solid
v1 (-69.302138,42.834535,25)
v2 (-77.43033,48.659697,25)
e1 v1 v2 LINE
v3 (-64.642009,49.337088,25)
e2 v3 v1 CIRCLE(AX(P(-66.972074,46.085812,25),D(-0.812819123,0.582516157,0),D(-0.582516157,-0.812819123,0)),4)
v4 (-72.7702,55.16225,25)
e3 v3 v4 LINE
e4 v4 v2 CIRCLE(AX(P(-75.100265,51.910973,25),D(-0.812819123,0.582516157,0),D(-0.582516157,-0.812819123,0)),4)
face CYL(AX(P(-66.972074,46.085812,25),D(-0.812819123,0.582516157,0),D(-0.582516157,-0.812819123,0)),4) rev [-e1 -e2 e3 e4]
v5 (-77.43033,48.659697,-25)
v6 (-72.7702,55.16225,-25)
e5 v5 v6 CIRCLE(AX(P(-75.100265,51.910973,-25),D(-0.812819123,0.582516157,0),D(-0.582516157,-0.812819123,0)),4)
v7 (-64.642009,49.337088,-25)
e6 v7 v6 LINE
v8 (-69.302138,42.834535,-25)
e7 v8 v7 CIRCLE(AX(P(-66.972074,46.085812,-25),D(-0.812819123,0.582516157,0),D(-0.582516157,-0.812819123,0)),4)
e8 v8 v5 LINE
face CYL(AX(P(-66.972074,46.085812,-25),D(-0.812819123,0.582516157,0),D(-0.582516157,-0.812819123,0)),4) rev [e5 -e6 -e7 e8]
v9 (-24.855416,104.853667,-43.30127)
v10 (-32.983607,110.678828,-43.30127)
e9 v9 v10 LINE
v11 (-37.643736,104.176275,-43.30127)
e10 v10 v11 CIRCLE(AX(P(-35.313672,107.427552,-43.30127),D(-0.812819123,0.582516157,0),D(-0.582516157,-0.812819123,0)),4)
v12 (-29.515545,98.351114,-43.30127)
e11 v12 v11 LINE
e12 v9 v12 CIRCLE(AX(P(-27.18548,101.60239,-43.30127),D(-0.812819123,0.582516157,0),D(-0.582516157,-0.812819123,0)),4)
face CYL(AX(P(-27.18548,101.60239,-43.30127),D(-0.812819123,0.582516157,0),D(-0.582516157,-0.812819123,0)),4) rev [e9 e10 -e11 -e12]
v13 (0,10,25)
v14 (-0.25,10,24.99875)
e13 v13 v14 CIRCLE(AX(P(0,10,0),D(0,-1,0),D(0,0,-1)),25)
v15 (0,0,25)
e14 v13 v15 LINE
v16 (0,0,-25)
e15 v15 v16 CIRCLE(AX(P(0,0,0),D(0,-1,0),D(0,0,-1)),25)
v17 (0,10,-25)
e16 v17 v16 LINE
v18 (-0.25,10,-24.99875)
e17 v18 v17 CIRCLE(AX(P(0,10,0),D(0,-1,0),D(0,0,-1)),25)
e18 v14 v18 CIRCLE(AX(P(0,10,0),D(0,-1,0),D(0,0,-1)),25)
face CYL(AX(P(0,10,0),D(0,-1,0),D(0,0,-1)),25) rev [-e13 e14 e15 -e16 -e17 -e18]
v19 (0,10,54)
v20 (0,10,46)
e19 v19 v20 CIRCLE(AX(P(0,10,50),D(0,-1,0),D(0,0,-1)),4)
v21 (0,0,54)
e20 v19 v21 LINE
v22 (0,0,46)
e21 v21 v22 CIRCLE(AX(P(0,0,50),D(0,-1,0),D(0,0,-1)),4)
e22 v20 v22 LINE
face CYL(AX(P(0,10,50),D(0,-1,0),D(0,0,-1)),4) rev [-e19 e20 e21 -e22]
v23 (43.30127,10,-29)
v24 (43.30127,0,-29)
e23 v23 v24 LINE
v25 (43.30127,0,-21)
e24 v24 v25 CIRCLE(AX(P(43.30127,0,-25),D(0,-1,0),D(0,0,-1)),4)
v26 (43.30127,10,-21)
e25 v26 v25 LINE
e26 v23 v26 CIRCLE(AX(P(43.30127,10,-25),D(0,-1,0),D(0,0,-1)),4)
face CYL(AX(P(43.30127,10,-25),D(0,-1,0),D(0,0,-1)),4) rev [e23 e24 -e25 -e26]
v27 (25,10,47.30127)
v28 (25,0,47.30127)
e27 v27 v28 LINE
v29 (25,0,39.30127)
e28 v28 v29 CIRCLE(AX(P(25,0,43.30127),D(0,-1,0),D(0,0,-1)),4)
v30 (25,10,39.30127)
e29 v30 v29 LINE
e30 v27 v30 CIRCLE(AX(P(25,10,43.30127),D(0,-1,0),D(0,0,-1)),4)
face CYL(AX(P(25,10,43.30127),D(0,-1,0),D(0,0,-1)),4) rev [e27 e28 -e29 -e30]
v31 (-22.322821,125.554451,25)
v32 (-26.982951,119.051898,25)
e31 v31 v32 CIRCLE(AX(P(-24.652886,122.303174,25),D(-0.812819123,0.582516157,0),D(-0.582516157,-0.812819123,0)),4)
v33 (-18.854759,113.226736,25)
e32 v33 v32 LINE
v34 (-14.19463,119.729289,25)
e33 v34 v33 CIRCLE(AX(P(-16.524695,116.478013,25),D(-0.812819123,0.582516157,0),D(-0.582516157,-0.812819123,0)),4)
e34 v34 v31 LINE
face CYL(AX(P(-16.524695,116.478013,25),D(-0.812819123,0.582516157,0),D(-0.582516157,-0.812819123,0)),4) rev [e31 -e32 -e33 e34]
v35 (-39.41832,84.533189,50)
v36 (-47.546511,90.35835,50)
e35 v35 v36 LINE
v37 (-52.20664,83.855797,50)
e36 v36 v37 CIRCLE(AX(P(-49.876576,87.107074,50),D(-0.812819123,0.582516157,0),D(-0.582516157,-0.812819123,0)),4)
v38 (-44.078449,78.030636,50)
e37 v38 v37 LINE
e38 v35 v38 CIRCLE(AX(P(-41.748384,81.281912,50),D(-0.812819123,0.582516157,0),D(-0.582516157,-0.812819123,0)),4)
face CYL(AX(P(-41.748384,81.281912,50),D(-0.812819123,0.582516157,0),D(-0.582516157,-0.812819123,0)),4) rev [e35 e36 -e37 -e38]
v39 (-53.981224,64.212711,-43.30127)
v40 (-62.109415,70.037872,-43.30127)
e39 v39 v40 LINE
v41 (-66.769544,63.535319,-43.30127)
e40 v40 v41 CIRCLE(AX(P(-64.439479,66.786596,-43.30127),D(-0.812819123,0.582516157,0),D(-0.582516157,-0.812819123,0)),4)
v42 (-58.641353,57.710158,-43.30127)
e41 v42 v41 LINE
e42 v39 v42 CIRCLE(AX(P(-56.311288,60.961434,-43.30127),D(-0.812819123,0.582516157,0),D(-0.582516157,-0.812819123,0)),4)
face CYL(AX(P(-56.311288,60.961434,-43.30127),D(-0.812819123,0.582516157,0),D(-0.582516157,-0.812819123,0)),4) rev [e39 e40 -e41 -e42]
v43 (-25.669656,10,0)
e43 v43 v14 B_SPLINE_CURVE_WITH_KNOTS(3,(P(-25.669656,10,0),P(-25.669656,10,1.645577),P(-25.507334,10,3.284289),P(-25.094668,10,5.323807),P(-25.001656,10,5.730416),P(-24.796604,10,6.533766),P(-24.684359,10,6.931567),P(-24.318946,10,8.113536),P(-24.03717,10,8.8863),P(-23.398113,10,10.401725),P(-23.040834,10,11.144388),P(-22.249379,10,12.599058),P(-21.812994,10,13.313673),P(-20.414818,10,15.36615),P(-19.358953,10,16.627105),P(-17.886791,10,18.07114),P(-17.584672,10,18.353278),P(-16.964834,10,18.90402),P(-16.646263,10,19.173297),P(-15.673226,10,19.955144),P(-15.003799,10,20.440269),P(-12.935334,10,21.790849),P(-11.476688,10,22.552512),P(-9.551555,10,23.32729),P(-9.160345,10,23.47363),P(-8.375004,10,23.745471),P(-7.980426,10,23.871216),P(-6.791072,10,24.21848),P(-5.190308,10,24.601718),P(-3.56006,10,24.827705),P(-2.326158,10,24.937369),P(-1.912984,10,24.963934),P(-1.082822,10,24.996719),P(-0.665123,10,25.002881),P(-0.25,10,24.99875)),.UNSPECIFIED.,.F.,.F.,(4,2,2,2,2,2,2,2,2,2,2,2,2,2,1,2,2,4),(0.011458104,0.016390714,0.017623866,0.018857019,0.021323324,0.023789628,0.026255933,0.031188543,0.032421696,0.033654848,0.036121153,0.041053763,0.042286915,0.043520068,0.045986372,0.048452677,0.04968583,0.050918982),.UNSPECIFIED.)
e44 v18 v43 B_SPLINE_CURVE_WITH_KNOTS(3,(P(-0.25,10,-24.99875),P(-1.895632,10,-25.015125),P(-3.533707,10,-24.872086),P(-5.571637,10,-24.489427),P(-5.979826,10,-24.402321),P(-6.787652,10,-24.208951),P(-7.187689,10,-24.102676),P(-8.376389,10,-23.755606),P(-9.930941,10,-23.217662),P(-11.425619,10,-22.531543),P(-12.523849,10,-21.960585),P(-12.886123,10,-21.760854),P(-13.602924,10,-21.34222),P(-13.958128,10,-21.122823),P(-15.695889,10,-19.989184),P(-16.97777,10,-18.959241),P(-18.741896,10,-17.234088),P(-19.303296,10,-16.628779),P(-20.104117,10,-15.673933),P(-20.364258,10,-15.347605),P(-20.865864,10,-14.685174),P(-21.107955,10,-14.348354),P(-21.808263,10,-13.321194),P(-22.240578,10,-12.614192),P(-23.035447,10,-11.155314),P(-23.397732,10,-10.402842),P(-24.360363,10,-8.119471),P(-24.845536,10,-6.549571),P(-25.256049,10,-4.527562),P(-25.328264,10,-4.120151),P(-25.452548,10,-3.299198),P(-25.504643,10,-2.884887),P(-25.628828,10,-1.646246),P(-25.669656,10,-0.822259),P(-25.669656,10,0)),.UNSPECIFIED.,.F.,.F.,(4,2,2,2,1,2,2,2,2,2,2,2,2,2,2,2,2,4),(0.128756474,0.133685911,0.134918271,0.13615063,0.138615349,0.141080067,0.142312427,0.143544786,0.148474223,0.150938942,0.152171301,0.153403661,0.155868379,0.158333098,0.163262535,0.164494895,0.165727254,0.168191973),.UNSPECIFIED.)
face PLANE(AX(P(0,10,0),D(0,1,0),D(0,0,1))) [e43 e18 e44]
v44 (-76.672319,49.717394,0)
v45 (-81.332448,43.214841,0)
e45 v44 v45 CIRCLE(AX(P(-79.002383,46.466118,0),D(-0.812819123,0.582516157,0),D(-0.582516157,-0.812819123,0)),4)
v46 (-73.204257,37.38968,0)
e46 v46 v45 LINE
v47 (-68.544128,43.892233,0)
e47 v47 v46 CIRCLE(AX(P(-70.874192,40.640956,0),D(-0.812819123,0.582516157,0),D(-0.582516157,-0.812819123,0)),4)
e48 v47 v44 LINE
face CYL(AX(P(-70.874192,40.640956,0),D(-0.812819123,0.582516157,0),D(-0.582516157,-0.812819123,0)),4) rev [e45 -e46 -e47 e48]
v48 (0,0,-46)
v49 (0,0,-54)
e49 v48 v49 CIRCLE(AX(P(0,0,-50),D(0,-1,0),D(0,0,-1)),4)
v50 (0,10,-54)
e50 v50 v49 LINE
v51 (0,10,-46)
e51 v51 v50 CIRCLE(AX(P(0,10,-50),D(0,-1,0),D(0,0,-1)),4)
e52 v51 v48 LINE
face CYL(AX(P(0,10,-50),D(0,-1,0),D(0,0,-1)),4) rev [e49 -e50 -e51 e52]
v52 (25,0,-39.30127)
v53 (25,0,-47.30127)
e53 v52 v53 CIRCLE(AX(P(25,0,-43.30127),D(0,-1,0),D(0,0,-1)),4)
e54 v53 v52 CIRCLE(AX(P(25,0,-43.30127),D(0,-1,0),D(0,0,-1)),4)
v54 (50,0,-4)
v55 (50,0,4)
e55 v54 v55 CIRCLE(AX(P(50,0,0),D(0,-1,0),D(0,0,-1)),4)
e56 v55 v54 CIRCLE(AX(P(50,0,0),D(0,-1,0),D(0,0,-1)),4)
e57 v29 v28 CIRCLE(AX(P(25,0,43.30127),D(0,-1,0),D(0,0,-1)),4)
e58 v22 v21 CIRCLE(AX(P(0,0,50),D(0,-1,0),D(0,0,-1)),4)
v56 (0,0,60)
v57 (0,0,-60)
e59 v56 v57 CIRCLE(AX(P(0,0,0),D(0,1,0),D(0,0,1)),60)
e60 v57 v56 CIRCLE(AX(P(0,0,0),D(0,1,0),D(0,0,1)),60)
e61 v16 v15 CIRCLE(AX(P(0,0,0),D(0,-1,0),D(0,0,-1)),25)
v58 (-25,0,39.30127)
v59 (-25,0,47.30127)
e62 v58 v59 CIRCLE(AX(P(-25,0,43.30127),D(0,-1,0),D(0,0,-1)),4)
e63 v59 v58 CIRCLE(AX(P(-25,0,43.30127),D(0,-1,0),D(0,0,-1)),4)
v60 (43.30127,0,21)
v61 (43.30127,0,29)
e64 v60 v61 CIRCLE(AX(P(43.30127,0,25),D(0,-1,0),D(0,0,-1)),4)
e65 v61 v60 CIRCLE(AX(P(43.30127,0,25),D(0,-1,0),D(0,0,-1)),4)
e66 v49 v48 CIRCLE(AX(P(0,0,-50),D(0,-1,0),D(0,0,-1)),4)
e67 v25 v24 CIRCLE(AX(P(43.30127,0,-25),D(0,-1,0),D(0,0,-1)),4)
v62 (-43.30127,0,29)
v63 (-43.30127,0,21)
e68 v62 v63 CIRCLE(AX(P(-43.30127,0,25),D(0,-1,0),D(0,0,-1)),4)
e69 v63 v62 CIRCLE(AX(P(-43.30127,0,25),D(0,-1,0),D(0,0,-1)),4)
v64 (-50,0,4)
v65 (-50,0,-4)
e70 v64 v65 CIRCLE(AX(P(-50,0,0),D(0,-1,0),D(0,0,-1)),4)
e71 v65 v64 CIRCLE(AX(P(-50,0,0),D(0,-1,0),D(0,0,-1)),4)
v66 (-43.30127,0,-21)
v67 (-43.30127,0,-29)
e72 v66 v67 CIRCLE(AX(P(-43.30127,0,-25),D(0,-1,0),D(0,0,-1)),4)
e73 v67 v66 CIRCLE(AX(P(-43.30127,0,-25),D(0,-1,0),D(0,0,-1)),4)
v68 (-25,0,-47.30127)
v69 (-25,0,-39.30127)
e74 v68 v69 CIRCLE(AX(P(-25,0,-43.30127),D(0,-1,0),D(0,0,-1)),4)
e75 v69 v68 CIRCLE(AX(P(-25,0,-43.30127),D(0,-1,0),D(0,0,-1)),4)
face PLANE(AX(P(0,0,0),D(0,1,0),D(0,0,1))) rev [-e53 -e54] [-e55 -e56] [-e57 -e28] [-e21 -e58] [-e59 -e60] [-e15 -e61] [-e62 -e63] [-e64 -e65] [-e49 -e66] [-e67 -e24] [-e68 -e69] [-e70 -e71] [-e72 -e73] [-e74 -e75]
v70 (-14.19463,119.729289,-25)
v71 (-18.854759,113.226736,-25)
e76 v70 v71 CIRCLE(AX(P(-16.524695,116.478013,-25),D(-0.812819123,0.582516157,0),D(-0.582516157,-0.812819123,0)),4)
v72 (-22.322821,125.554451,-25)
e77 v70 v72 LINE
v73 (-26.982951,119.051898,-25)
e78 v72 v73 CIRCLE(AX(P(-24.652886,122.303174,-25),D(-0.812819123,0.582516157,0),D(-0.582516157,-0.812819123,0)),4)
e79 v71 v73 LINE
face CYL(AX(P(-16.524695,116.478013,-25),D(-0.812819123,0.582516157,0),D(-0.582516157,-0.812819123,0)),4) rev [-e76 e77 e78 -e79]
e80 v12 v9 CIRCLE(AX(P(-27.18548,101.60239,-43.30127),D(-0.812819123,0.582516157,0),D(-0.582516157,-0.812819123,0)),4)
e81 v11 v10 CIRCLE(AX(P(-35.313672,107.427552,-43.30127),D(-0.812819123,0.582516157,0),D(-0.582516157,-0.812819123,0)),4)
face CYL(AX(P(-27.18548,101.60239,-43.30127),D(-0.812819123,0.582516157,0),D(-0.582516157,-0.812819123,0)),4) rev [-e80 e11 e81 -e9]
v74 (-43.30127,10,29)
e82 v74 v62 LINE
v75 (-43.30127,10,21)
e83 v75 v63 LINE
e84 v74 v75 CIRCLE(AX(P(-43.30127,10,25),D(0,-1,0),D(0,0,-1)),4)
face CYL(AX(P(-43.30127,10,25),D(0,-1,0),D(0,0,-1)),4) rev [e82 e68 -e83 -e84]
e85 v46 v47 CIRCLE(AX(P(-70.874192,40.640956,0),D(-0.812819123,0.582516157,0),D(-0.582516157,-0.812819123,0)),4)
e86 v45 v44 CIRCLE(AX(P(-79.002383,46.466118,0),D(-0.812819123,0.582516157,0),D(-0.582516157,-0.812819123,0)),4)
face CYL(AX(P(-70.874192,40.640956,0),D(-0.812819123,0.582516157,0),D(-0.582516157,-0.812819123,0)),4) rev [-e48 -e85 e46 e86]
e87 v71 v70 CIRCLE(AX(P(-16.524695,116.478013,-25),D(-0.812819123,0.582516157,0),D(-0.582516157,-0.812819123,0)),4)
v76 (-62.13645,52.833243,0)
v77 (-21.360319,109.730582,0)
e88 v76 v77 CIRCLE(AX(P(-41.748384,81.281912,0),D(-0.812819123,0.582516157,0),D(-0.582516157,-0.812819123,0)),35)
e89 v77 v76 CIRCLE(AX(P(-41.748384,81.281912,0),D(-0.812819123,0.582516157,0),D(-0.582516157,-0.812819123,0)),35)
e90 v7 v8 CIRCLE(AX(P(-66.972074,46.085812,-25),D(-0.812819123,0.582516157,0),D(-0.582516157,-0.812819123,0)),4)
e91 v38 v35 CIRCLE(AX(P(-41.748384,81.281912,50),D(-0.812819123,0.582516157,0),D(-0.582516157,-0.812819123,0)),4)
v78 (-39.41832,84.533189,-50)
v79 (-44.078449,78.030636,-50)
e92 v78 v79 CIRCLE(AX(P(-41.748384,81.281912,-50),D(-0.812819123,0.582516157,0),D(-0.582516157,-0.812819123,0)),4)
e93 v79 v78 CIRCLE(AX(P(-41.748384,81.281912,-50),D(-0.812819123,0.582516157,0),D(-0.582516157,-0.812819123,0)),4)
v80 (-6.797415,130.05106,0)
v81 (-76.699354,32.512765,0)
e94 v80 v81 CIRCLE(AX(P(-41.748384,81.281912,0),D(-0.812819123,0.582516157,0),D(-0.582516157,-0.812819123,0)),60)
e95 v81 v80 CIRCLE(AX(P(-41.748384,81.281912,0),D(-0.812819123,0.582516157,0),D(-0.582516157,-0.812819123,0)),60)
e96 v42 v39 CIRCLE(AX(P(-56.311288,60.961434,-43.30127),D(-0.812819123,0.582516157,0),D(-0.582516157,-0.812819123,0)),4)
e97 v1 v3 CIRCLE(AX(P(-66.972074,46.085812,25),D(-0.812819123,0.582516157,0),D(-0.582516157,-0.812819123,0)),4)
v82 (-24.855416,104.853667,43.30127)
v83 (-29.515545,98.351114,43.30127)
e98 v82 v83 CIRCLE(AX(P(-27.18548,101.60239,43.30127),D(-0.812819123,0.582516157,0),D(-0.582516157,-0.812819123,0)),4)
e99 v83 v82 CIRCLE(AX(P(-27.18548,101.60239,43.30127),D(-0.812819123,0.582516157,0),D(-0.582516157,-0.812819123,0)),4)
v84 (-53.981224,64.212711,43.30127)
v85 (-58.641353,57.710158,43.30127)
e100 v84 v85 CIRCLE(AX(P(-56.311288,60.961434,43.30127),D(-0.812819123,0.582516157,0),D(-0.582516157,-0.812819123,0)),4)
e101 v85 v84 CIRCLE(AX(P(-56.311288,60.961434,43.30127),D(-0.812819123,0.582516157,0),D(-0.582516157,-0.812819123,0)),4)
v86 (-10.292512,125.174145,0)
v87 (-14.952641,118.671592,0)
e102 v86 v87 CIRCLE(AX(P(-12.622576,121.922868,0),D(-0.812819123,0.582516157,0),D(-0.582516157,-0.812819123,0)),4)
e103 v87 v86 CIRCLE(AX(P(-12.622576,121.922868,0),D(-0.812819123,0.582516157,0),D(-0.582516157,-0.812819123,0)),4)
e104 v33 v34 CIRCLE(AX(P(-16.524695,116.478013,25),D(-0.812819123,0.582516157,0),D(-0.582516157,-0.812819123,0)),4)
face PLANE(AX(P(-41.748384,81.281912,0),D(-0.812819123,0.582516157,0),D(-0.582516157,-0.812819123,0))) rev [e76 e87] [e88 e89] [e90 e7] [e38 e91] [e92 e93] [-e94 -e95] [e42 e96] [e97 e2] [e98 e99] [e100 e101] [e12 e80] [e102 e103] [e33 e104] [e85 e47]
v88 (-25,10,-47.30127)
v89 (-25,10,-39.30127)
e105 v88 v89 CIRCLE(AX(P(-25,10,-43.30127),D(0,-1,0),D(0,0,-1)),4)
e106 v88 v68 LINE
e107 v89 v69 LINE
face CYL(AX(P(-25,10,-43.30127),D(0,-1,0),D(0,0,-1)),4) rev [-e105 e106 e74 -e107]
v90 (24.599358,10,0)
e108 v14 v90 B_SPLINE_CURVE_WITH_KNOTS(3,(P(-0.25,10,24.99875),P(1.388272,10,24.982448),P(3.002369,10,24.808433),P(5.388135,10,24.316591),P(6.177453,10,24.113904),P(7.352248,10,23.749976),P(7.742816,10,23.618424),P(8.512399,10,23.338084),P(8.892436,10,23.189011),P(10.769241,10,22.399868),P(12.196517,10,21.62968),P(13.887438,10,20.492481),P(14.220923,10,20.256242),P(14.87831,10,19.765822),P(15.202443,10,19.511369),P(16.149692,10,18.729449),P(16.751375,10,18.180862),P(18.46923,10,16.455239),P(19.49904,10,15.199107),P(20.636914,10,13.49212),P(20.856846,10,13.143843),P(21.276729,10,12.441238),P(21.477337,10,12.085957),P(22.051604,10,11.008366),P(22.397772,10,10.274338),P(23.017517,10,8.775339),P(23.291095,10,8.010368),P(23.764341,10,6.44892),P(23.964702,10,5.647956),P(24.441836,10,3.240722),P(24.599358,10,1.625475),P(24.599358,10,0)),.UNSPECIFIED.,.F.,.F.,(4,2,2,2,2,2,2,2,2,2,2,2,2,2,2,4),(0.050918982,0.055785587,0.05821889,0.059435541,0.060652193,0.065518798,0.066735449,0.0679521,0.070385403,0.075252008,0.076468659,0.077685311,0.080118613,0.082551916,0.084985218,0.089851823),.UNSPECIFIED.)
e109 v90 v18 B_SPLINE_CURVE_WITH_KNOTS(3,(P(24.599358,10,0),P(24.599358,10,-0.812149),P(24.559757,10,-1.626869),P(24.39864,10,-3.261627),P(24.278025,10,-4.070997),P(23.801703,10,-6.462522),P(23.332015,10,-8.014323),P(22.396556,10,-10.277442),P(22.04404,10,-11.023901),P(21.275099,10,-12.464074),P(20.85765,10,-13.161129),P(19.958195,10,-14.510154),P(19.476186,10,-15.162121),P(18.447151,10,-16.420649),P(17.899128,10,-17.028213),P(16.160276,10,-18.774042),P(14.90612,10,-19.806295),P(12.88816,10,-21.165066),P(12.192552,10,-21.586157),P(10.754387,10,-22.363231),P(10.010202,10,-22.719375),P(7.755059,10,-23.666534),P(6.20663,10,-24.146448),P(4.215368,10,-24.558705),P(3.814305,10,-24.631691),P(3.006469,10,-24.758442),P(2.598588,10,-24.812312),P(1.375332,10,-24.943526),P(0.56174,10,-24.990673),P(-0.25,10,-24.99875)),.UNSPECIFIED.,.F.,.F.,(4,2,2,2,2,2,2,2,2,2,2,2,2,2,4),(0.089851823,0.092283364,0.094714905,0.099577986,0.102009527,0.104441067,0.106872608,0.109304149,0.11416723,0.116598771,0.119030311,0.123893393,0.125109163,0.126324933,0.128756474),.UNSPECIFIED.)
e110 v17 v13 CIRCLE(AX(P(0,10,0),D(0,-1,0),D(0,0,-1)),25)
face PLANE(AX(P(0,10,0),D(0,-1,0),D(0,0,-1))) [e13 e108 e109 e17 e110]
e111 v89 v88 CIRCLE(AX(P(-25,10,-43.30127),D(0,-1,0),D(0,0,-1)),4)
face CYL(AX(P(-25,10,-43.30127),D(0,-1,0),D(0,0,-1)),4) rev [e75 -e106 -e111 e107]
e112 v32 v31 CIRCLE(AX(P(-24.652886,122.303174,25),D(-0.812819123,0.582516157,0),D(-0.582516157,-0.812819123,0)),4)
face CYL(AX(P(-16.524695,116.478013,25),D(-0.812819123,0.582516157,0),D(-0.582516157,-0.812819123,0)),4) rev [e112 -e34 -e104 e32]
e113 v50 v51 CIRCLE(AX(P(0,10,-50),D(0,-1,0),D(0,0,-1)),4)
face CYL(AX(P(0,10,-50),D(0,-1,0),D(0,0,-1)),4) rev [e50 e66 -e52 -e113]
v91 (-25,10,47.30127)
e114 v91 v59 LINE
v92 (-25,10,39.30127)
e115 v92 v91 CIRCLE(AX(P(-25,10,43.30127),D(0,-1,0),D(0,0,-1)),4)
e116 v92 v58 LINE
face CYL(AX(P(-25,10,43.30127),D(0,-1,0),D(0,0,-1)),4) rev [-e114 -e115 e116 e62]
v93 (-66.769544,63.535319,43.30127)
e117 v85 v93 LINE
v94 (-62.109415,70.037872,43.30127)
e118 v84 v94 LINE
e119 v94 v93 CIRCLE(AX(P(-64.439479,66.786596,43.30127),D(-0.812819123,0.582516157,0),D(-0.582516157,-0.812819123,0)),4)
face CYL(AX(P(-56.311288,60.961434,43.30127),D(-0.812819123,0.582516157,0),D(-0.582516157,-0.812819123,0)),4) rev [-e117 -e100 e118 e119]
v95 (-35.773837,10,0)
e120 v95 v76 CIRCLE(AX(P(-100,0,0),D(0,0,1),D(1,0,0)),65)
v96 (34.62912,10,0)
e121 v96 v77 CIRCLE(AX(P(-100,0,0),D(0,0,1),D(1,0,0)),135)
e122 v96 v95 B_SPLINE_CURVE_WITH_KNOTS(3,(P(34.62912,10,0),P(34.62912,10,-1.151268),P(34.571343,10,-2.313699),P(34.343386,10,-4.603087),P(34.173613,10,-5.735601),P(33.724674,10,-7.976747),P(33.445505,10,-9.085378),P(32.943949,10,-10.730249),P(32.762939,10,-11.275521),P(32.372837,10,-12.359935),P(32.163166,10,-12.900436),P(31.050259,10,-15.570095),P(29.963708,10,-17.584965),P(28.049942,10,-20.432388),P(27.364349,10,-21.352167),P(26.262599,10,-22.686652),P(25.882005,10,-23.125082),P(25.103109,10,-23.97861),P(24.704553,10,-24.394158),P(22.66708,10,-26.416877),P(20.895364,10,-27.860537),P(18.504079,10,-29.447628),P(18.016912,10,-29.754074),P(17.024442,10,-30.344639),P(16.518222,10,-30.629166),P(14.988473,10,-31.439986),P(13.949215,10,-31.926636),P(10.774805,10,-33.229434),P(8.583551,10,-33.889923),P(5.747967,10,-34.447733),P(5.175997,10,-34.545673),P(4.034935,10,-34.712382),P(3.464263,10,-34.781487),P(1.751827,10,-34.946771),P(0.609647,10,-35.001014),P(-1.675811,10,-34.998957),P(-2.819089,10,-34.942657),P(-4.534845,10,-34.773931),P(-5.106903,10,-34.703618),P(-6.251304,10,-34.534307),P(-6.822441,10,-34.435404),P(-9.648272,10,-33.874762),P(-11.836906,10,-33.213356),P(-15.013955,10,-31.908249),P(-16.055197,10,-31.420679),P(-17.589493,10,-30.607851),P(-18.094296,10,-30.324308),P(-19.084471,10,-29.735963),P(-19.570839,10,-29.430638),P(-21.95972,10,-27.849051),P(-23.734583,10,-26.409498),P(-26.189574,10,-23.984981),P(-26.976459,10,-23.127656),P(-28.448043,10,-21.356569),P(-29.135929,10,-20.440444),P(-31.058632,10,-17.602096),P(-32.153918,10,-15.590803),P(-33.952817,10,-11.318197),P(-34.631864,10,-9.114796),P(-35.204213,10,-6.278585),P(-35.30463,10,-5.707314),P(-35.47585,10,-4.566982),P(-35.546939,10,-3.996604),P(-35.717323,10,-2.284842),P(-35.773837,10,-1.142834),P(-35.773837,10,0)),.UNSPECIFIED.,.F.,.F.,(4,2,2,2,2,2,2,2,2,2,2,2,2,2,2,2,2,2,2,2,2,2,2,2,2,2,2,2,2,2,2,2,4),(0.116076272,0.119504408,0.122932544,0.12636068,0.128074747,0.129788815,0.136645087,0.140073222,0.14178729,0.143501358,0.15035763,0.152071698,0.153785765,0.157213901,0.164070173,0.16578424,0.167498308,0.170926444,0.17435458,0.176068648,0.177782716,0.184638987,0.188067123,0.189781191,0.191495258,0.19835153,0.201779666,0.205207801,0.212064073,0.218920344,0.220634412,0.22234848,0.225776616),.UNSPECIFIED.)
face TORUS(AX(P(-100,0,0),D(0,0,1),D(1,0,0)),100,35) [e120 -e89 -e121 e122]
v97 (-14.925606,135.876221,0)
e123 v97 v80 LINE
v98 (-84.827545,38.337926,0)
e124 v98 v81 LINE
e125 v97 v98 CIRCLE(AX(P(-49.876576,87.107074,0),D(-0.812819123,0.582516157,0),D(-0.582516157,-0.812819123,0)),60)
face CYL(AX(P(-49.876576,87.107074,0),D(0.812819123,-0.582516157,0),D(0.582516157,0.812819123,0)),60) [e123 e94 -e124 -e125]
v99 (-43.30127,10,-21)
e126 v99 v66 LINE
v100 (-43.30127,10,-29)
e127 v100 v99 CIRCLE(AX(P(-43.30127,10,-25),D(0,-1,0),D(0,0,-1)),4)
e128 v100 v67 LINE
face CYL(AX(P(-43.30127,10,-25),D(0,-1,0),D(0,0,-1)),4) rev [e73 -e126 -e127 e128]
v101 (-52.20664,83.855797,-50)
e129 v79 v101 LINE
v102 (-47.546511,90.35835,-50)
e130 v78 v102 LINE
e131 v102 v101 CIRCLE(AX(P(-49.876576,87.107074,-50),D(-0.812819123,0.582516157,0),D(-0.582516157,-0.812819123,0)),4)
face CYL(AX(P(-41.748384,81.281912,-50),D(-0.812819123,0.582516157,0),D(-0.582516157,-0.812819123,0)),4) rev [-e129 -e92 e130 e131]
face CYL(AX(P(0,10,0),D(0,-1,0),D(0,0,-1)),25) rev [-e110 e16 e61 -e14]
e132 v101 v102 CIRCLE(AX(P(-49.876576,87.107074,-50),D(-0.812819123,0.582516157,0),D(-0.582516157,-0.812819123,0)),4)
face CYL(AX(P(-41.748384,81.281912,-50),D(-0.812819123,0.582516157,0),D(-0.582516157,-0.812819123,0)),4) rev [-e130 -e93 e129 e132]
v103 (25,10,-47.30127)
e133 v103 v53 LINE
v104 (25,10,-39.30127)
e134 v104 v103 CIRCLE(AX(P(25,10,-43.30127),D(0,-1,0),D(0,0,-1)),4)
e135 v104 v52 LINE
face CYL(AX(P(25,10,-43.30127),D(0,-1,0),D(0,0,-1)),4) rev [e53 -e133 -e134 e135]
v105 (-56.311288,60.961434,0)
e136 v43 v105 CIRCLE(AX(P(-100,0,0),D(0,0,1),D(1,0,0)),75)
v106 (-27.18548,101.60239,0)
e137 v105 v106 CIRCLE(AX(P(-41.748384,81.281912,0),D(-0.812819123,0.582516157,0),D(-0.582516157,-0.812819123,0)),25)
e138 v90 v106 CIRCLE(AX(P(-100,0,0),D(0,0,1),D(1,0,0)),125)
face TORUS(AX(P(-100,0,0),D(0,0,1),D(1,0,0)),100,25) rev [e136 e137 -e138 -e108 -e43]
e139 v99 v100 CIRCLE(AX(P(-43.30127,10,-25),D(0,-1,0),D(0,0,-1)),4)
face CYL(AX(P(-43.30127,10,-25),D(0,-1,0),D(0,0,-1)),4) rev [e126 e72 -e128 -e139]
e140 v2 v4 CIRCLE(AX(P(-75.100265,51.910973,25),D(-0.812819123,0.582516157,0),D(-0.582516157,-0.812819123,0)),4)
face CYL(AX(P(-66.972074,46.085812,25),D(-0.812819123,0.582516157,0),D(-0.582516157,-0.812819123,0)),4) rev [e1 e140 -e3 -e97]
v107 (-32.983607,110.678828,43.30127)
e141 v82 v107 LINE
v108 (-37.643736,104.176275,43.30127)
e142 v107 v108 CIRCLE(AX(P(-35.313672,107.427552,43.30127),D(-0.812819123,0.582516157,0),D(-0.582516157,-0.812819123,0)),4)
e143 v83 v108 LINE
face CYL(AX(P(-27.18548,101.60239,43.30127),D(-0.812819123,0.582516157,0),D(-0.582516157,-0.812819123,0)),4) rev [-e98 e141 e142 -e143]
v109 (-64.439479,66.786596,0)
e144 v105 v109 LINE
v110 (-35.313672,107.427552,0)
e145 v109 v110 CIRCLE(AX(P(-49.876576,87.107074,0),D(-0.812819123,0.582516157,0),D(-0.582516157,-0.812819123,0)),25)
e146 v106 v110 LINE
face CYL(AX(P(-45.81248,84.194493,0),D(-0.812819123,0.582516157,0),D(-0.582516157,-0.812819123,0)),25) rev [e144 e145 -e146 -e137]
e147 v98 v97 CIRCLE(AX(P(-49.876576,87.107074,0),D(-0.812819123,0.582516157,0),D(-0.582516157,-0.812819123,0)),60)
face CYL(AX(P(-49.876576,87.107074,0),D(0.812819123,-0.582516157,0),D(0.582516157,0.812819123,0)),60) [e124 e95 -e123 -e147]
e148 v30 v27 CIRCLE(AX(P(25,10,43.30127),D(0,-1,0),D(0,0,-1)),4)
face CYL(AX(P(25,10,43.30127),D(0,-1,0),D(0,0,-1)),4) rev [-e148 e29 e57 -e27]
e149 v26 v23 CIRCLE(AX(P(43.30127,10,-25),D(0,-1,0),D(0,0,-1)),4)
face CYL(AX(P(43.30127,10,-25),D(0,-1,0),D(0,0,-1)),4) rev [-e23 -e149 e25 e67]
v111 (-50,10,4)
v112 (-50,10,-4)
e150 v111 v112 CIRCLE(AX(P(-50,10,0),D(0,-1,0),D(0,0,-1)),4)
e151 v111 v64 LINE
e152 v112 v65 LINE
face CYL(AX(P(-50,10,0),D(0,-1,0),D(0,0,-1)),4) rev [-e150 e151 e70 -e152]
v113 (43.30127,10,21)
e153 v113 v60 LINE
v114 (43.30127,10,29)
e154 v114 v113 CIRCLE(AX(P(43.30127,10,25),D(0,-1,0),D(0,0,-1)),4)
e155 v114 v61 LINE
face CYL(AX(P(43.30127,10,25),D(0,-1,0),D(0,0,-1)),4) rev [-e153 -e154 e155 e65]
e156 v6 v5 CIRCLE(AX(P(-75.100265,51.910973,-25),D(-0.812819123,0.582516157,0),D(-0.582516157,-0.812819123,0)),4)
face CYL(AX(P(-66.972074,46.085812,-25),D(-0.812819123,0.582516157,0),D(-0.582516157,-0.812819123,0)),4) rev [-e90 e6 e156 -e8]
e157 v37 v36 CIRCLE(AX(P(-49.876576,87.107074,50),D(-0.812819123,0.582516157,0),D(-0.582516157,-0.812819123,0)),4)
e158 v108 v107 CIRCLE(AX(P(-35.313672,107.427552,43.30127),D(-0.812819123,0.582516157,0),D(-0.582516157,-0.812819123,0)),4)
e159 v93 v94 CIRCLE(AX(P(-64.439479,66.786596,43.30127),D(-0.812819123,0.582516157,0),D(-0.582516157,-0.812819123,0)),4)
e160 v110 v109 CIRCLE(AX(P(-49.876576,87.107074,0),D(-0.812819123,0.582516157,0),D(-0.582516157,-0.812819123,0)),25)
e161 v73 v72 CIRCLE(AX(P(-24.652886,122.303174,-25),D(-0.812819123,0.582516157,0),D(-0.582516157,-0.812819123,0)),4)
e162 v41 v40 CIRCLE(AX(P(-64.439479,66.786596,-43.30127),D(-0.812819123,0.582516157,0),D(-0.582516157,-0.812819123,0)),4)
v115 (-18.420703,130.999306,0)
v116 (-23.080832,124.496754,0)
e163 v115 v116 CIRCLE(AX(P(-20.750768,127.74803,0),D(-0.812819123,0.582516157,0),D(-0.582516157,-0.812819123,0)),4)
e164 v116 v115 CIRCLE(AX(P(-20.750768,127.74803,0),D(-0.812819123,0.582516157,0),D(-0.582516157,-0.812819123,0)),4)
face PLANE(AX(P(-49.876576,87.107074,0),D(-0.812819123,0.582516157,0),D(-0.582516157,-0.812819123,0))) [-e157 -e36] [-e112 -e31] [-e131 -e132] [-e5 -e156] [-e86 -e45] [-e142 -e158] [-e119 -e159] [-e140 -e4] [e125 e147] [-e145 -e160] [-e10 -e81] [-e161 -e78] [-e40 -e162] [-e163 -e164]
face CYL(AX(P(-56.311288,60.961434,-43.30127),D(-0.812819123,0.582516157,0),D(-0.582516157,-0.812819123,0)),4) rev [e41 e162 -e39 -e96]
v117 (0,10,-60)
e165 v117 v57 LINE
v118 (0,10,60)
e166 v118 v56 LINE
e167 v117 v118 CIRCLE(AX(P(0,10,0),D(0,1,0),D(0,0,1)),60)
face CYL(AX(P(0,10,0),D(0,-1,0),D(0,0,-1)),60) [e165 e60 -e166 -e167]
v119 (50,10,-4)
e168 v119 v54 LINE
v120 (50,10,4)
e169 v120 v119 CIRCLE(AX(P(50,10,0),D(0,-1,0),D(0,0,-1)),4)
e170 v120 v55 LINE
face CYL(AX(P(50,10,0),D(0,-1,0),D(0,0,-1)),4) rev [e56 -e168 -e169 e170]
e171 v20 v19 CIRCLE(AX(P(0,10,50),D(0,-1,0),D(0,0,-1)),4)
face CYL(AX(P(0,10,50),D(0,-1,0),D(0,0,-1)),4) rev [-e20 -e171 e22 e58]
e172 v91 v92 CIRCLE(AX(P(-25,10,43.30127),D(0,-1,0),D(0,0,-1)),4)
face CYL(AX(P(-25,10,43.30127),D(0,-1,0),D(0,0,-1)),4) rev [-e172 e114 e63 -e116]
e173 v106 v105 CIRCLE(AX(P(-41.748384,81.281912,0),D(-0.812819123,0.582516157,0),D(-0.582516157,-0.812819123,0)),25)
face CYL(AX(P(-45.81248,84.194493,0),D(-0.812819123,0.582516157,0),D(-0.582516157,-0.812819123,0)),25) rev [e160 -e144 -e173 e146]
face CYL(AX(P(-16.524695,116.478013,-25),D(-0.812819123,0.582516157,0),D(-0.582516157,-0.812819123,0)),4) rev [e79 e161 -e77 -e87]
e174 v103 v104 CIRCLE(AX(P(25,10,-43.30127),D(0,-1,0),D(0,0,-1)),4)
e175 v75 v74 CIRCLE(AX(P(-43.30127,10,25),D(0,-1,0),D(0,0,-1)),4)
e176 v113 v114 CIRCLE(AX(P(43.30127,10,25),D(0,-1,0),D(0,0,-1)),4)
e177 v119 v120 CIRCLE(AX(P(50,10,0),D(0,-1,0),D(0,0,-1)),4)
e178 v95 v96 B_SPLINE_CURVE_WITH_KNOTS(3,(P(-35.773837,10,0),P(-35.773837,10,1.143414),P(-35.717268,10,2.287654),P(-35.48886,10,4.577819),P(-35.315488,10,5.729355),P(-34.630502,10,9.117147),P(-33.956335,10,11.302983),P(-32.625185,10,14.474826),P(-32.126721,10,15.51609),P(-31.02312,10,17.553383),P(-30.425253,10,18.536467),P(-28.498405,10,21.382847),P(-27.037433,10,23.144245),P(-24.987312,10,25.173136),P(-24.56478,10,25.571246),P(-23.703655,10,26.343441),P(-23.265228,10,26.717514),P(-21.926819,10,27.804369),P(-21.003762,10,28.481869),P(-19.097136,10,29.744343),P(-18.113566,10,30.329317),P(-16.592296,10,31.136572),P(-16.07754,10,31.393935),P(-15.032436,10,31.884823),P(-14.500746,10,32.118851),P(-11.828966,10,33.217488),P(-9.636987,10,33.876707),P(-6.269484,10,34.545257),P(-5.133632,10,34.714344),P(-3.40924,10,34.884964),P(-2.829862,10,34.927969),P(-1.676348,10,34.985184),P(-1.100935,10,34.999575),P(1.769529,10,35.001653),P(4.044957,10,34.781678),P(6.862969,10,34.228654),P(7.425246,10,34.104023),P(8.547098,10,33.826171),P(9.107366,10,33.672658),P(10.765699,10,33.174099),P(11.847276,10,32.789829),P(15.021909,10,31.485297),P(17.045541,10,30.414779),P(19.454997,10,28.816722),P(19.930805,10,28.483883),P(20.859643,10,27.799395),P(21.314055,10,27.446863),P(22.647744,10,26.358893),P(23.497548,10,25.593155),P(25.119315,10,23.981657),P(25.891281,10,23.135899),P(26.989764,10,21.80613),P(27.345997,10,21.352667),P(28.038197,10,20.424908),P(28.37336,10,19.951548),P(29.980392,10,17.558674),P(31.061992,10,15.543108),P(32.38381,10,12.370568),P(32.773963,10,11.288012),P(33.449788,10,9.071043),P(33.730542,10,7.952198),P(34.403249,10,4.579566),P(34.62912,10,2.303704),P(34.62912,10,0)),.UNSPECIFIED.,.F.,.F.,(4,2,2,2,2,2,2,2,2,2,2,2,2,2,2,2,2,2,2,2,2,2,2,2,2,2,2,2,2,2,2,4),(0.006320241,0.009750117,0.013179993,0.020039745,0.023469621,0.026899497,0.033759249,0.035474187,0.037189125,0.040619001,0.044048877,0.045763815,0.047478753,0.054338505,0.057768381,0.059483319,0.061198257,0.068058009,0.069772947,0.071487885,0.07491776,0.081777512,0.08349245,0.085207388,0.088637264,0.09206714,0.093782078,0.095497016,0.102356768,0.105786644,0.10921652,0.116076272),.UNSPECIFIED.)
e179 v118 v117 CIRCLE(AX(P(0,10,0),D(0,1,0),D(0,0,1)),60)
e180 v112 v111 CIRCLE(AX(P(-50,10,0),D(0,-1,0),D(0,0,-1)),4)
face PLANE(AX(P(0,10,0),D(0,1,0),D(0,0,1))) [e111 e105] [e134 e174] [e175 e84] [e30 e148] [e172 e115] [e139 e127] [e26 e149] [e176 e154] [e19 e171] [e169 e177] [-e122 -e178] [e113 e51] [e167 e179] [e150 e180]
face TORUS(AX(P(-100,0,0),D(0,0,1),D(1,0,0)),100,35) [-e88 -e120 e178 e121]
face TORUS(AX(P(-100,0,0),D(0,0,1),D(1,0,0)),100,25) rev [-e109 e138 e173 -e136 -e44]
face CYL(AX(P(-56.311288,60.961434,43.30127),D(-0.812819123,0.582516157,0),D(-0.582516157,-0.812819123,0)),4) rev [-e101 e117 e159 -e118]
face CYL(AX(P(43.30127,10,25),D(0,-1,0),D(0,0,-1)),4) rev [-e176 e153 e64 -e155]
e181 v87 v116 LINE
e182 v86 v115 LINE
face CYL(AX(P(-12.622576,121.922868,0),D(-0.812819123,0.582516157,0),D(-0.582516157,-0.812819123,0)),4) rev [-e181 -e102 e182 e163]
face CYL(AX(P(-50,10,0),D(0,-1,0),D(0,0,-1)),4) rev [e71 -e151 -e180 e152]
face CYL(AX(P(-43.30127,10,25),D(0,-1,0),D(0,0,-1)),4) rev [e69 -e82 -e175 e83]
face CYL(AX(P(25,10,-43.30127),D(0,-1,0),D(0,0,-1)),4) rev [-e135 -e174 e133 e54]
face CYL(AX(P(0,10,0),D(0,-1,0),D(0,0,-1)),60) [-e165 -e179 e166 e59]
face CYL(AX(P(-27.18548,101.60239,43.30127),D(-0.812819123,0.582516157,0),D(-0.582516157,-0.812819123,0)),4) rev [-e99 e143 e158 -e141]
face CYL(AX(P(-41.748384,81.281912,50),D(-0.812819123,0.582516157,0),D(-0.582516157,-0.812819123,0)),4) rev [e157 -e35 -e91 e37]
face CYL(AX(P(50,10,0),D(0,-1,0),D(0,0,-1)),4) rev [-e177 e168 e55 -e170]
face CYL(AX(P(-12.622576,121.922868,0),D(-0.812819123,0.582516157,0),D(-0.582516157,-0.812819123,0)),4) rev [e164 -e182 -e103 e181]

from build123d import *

# Parameters (mm, degrees)
BOTTOM_FLANGE_PROFILE_R            = 60
BOTTOM_FLANGE_120_DEPTH            = 10
ELBOW_PIPE_SWEEP_PROFILE_R         = 35
ELBOW_PIPE_SWEEP_PROFILE_R_2       = 25
TOP_FLANGE_PROFILE_R               = 60
TOP_FLANGE_120_DEPTH               = 10
TOP_BORE_PROFILE_A_R               = 25
TOP_FLANGE_BORE_CUT_A_DEPTH        = 5
TOP_BORE_PROFILE_B_R               = 25
TOP_FLANGE_BORE_CUT_B_DEPTH        = 5
BOTTOM_BORE_PROFILE_R              = 25
BOTTOM_FLANGE_BORE_DEPTH           = 10
TOP_BOLT_HOLE_CIRCLE_R             = 4
TOP_FLANGE_BOLT_HOLES_12X_DEPTH    = 10
BOTTOM_BOLT_HOLE_CIRCLE_R          = 4
BOTTOM_FLANGE_BOLT_HOLES_12X_DEPTH = 10


with BuildPart() as part:
    # Bottom Flange Profile → Bottom Flange _120 (new body)
    with BuildSketch(Plane(origin=(0, 0, 0), x_dir=(1, 0, 0), z_dir=(0, 1, 0))):
        with Locations(Location((0, 0, 0), (0, 0, 270))):
            Circle(BOTTOM_FLANGE_PROFILE_R)
    extrude(amount=BOTTOM_FLANGE_120_DEPTH)

    # Elbow Pipe Sweep: sweep along a path in Elbow Bend Path
    with BuildLine(Plane.XY) as elbow_pipe_sweep_path:
        ThreePointArc((0, 0), (-11.047311529, 45.688283112), (-41.748384274, 81.281912289))
    # Elbow Pipe Sweep profile (on start of the path) → Elbow Pipe Sweep (sweep)
    with BuildSketch(Plane(origin=(0, 0, 0), x_dir=(1, 0, 0), z_dir=(0, 1, 0))):
        Circle(ELBOW_PIPE_SWEEP_PROFILE_R)
        Circle(ELBOW_PIPE_SWEEP_PROFILE_R_2, mode=Mode.SUBTRACT)
    sweep(path=elbow_pipe_sweep_path.line)

    # Top Flange Profile → Top Flange _120 (add)
    with BuildSketch(Plane(origin=(-66.067492653, 47.348027201, 0), x_dir=(0, 0, 1), z_dir=(-0.8128191228882113, 0.5825161572585252, 0))):
        with Locations(Location((0, 41.748384274, 0), (0, 0, 270))):
            Circle(TOP_FLANGE_PROFILE_R)
    extrude(amount=TOP_FLANGE_120_DEPTH)

    # Top Bore Profile A → Top Flange Bore Cut A (cut)
    with BuildSketch(Plane(origin=(-74.195683882, 53.173188774, 0), x_dir=(0, 0, 1), z_dir=(-0.8128191228882113, 0.5825161572585252, 0))):
        with Locations(Location((0, 41.748384274, 0), (0, 0, 270))):
            Circle(TOP_BORE_PROFILE_A_R)
    extrude(amount=-TOP_FLANGE_BORE_CUT_A_DEPTH, mode=Mode.SUBTRACT)

    # Top Bore Profile B → Top Flange Bore Cut B (cut)
    with BuildSketch(Plane(origin=(-70.131588268, 50.260607987, 0), x_dir=(0, 0, 1), z_dir=(-0.8128191228882113, 0.5825161572585252, 0))):
        with Locations(Location((0, 41.748384274, 0), (0, 0, 270))):
            Circle(TOP_BORE_PROFILE_B_R)
    extrude(amount=-TOP_FLANGE_BORE_CUT_B_DEPTH, mode=Mode.SUBTRACT)

    # Bottom Bore Profile → Bottom Flange Bore (cut)
    with BuildSketch(Plane.XZ):
        with Locations(Location((0, 0, 0), (0, 0, 270))):
            Circle(BOTTOM_BORE_PROFILE_R)
    extrude(amount=-BOTTOM_FLANGE_BORE_DEPTH, mode=Mode.SUBTRACT)

    # Top Bolt Hole Circle → Top Flange Bolt Holes 12x (cut)
    with BuildSketch(Plane(origin=(-74.195683882, 53.173188774, 0), x_dir=(0, 0, 1), z_dir=(-0.8128191228882113, 0.5825161572585252, 0))):
        with Locations(Location((0, 91.748384274, 0), (0, 0, 270))):
            Circle(TOP_BOLT_HOLE_CIRCLE_R)
        with Locations(Location((25, 85.049654463, 0), (0, 0, 270))):
            Circle(TOP_BOLT_HOLE_CIRCLE_R)
        with Locations(Location((43.301270189, 66.748384274, 0), (0, 0, 270))):
            Circle(TOP_BOLT_HOLE_CIRCLE_R)
        with Locations(Location((50, 41.748384274, 0), (0, 0, 270))):
            Circle(TOP_BOLT_HOLE_CIRCLE_R)
        with Locations(Location((43.301270189, 16.748384274, 0), (0, 0, 270))):
            Circle(TOP_BOLT_HOLE_CIRCLE_R)
        with Locations(Location((25, -1.552885915, 0), (0, 0, 270))):
            Circle(TOP_BOLT_HOLE_CIRCLE_R)
        with Locations(Location((0, -8.251615726, 0), (0, 0, 270))):
            Circle(TOP_BOLT_HOLE_CIRCLE_R)
        with Locations(Location((-25, -1.552885915, 0), (0, 0, 270))):
            Circle(TOP_BOLT_HOLE_CIRCLE_R)
        with Locations(Location((-43.301270189, 16.748384274, 0), (0, 0, 270))):
            Circle(TOP_BOLT_HOLE_CIRCLE_R)
        with Locations(Location((-50, 41.748384274, 0), (0, 0, 270))):
            Circle(TOP_BOLT_HOLE_CIRCLE_R)
        with Locations(Location((-43.301270189, 66.748384274, 0), (0, 0, 270))):
            Circle(TOP_BOLT_HOLE_CIRCLE_R)
        with Locations(Location((-25, 85.049654463, 0), (0, 0, 270))):
            Circle(TOP_BOLT_HOLE_CIRCLE_R)
    extrude(amount=-TOP_FLANGE_BOLT_HOLES_12X_DEPTH, mode=Mode.SUBTRACT)

    # Bottom Bolt Hole Circle → Bottom Flange Bolt Holes 12x (cut)
    with BuildSketch(Plane.XZ):
        with Locations(Location((0, 50, 0), (0, 0, 270))):
            Circle(BOTTOM_BOLT_HOLE_CIRCLE_R)
        with Locations(Location((25, 43.301270189, 0), (0, 0, 270))):
            Circle(BOTTOM_BOLT_HOLE_CIRCLE_R)
        with Locations(Location((43.301270189, 25, 0), (0, 0, 270))):
            Circle(BOTTOM_BOLT_HOLE_CIRCLE_R)
        with Locations(Location((50, 0, 0), (0, 0, 270))):
            Circle(BOTTOM_BOLT_HOLE_CIRCLE_R)
        with Locations(Location((43.301270189, -25, 0), (0, 0, 270))):
            Circle(BOTTOM_BOLT_HOLE_CIRCLE_R)
        with Locations(Location((25, -43.301270189, 0), (0, 0, 270))):
            Circle(BOTTOM_BOLT_HOLE_CIRCLE_R)
        with Locations(Location((0, -50, 0), (0, 0, 270))):
            Circle(BOTTOM_BOLT_HOLE_CIRCLE_R)
        with Locations(Location((-25, -43.301270189, 0), (0, 0, 270))):
            Circle(BOTTOM_BOLT_HOLE_CIRCLE_R)
        with Locations(Location((-43.301270189, -25, 0), (0, 0, 270))):
            Circle(BOTTOM_BOLT_HOLE_CIRCLE_R)
        with Locations(Location((-50, 0, 0), (0, 0, 270))):
            Circle(BOTTOM_BOLT_HOLE_CIRCLE_R)
        with Locations(Location((-43.301270189, 25, 0), (0, 0, 270))):
            Circle(BOTTOM_BOLT_HOLE_CIRCLE_R)
        with Locations(Location((-25, 43.301270189, 0), (0, 0, 270))):
            Circle(BOTTOM_BOLT_HOLE_CIRCLE_R)
    extrude(amount=-BOTTOM_FLANGE_BOLT_HOLES_12X_DEPTH, mode=Mode.SUBTRACT)


solid = part.part
